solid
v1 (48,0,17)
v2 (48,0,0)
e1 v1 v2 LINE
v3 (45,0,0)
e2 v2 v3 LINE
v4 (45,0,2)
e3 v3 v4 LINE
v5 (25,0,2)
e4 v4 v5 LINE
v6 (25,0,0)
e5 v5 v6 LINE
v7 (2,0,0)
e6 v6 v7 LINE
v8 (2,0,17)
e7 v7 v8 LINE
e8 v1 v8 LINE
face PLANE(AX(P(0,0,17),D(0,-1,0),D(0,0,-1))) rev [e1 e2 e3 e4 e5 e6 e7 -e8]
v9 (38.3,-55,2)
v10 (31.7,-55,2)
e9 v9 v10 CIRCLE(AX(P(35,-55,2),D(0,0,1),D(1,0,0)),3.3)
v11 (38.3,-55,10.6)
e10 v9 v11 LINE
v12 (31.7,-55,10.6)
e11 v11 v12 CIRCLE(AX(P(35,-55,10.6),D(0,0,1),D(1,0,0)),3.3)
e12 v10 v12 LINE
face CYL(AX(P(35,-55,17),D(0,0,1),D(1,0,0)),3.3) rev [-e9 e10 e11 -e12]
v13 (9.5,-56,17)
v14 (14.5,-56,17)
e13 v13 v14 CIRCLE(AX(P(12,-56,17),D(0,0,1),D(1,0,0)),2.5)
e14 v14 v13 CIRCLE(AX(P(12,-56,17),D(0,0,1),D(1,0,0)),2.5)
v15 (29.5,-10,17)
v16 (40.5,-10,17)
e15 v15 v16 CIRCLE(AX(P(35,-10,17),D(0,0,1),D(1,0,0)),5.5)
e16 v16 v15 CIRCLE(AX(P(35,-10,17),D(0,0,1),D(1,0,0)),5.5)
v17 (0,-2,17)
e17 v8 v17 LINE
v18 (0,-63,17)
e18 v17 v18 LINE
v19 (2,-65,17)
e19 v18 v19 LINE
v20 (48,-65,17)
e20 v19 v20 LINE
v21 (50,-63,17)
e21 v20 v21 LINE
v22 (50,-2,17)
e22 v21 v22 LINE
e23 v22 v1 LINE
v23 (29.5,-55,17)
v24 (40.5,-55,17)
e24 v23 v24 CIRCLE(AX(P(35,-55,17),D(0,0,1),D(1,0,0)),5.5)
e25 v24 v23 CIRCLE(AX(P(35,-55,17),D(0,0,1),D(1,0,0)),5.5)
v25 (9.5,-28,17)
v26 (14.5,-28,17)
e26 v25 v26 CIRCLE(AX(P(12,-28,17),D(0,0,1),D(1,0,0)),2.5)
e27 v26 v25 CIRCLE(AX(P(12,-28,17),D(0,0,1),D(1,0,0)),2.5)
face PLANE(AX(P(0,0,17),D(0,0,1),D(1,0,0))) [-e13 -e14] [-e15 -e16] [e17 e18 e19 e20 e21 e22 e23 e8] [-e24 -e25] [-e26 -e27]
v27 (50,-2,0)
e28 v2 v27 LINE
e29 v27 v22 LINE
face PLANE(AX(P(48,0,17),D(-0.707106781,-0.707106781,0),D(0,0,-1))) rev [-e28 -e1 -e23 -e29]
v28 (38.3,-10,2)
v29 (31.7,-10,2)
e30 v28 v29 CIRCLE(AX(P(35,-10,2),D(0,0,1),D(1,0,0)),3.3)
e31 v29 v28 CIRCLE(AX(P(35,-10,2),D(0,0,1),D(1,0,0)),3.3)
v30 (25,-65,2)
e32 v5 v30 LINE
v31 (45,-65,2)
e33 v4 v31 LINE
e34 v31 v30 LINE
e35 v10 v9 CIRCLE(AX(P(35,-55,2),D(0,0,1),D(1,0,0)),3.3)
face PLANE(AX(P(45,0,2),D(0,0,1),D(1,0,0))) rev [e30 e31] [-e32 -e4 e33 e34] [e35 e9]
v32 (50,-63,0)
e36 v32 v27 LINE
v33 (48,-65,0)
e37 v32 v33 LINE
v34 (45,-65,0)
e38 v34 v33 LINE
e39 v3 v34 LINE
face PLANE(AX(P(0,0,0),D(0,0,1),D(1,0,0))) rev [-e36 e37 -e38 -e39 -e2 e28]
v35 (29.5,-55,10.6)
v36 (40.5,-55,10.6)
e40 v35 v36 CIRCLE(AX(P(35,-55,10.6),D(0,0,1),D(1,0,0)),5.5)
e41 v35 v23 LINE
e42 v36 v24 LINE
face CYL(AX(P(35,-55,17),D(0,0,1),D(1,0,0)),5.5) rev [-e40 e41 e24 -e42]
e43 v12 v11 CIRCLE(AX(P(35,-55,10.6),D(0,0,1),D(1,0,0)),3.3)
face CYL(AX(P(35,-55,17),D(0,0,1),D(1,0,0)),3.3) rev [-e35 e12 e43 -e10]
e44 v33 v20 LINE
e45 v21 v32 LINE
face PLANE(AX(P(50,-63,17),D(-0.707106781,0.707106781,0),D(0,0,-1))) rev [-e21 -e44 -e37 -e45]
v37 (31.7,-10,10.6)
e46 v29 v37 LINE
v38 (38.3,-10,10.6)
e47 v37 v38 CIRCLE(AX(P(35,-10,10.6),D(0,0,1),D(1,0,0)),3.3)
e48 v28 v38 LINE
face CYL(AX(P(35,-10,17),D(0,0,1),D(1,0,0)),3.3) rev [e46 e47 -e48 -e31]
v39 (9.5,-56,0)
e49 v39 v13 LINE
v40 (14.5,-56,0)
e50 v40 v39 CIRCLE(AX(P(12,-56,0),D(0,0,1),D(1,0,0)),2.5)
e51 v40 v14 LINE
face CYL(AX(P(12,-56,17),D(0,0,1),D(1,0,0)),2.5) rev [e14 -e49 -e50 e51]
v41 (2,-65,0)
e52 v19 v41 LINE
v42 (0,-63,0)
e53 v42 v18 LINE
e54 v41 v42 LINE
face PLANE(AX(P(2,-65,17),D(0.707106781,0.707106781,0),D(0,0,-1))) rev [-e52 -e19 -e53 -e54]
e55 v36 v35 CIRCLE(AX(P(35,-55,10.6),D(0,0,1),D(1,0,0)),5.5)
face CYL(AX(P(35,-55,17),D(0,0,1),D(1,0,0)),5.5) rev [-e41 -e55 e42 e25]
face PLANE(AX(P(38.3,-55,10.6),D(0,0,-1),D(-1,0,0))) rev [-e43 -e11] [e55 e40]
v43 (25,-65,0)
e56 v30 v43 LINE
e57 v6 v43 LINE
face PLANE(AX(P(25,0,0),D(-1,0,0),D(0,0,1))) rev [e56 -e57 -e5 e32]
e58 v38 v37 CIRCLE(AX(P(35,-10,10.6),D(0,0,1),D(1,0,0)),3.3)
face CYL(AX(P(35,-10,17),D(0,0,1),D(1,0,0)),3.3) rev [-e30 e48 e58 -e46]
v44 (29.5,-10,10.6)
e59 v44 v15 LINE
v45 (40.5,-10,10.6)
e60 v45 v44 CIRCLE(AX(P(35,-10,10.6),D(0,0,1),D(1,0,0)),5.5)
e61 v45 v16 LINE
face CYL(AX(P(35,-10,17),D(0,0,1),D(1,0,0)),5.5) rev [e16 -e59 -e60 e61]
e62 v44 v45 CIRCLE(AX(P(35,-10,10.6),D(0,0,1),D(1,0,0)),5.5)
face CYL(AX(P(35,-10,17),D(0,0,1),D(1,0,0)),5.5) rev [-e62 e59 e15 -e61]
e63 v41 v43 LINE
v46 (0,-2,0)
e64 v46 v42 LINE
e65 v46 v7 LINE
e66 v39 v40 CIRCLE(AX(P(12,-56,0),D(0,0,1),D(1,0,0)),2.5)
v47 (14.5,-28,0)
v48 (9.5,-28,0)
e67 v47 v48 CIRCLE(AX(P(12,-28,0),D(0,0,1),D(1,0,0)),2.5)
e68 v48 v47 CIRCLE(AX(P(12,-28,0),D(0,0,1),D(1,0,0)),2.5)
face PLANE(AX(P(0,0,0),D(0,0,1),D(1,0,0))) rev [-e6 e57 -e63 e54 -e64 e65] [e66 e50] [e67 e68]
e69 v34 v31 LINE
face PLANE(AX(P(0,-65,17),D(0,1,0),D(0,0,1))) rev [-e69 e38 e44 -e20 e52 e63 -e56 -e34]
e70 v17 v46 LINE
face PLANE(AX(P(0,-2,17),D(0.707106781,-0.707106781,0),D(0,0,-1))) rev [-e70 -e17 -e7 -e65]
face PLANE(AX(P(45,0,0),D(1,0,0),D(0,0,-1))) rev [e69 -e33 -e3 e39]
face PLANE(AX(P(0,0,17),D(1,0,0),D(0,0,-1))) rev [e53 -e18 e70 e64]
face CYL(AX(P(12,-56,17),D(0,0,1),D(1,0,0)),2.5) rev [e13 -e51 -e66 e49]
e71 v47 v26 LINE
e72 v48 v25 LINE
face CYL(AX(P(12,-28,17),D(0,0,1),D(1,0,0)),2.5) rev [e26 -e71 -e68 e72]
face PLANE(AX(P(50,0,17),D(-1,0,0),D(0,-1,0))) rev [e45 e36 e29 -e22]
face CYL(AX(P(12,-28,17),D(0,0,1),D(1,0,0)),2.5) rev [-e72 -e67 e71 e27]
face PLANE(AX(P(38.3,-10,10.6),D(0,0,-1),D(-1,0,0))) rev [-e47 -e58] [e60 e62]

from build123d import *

# Parameters (mm, degrees)
SKETCH_2_W                     = 50
SKETCH_2_H                     = 65
EXTRUDE_1_DEPTH                = 17
SKETCH_3_W                     = 20
SKETCH_3_H                     = 2
CUT_EXTRUDE_1_DEPTH            = 84.749626865
CHAMFER_1_SIZE                 = 2
HOLE_WIZARD_M6_1_D             = 5
HOLE_WIZARD_M6_1_DEPTH         = 17
HOLE_WIZARD_M6_1_TIP           = 1.502151548
HOLE_WIZARD_M6_1_2_D           = 6.6
HOLE_WIZARD_M6_1_2_DEPTH       = 17
HOLE_WIZARD_M6_1_2_CBORE_D     = 11
HOLE_WIZARD_M6_1_2_CBORE_DEPTH = 6.4
HOLE_WIZARD_M6_1_2_TIP         = 1.982840043


with BuildPart() as part:
    # 草图2 → 凸台-拉伸1 (new body)
    with BuildSketch(Plane.XY):
        with Locations((25, -32.5)):
            Rectangle(SKETCH_2_W, SKETCH_2_H)
    extrude(amount=EXTRUDE_1_DEPTH)

    # 草图3 → 切除-拉伸1 (cut, through all)
    with BuildSketch(Plane.XZ.offset(65)):
        with Locations((35, 1)):
            Rectangle(SKETCH_3_W, SKETCH_3_H)
    extrude(amount=-CUT_EXTRUDE_1_DEPTH, mode=Mode.SUBTRACT)

    # 倒角1
    chamfer_1_edges = [part.edges().sort_by_distance(p)[0] for p in [
        (0, 0, 8.5),
        (50, 0, 8.5),
        (50, -65, 8.5),
        (0, -65, 8.5),
    ]]
    chamfer(chamfer_1_edges, length=CHAMFER_1_SIZE)

    # Hole Wizard M6 _1
    with Locations(Plane.XY.offset(17)):
        with Locations((12, -28), (12, -56)):
            Hole(HOLE_WIZARD_M6_1_D / 2, depth=HOLE_WIZARD_M6_1_DEPTH)
            with Locations((0, 0, -(HOLE_WIZARD_M6_1_DEPTH + HOLE_WIZARD_M6_1_TIP / 2))):  # 118° drill point
                Cone(0, HOLE_WIZARD_M6_1_D / 2, HOLE_WIZARD_M6_1_TIP, mode=Mode.SUBTRACT)

    # Hole Wizard M6 _1 2
    with Locations(Plane.XY.offset(17)):
        with Locations((35, -10), (35, -55)):
            CounterBoreHole(HOLE_WIZARD_M6_1_2_D / 2, HOLE_WIZARD_M6_1_2_CBORE_D / 2, HOLE_WIZARD_M6_1_2_CBORE_DEPTH, depth=HOLE_WIZARD_M6_1_2_DEPTH)
            with Locations((0, 0, -(HOLE_WIZARD_M6_1_2_DEPTH + HOLE_WIZARD_M6_1_2_TIP / 2))):  # 118° drill point
                Cone(0, HOLE_WIZARD_M6_1_2_D / 2, HOLE_WIZARD_M6_1_2_TIP, mode=Mode.SUBTRACT)


solid = part.part
